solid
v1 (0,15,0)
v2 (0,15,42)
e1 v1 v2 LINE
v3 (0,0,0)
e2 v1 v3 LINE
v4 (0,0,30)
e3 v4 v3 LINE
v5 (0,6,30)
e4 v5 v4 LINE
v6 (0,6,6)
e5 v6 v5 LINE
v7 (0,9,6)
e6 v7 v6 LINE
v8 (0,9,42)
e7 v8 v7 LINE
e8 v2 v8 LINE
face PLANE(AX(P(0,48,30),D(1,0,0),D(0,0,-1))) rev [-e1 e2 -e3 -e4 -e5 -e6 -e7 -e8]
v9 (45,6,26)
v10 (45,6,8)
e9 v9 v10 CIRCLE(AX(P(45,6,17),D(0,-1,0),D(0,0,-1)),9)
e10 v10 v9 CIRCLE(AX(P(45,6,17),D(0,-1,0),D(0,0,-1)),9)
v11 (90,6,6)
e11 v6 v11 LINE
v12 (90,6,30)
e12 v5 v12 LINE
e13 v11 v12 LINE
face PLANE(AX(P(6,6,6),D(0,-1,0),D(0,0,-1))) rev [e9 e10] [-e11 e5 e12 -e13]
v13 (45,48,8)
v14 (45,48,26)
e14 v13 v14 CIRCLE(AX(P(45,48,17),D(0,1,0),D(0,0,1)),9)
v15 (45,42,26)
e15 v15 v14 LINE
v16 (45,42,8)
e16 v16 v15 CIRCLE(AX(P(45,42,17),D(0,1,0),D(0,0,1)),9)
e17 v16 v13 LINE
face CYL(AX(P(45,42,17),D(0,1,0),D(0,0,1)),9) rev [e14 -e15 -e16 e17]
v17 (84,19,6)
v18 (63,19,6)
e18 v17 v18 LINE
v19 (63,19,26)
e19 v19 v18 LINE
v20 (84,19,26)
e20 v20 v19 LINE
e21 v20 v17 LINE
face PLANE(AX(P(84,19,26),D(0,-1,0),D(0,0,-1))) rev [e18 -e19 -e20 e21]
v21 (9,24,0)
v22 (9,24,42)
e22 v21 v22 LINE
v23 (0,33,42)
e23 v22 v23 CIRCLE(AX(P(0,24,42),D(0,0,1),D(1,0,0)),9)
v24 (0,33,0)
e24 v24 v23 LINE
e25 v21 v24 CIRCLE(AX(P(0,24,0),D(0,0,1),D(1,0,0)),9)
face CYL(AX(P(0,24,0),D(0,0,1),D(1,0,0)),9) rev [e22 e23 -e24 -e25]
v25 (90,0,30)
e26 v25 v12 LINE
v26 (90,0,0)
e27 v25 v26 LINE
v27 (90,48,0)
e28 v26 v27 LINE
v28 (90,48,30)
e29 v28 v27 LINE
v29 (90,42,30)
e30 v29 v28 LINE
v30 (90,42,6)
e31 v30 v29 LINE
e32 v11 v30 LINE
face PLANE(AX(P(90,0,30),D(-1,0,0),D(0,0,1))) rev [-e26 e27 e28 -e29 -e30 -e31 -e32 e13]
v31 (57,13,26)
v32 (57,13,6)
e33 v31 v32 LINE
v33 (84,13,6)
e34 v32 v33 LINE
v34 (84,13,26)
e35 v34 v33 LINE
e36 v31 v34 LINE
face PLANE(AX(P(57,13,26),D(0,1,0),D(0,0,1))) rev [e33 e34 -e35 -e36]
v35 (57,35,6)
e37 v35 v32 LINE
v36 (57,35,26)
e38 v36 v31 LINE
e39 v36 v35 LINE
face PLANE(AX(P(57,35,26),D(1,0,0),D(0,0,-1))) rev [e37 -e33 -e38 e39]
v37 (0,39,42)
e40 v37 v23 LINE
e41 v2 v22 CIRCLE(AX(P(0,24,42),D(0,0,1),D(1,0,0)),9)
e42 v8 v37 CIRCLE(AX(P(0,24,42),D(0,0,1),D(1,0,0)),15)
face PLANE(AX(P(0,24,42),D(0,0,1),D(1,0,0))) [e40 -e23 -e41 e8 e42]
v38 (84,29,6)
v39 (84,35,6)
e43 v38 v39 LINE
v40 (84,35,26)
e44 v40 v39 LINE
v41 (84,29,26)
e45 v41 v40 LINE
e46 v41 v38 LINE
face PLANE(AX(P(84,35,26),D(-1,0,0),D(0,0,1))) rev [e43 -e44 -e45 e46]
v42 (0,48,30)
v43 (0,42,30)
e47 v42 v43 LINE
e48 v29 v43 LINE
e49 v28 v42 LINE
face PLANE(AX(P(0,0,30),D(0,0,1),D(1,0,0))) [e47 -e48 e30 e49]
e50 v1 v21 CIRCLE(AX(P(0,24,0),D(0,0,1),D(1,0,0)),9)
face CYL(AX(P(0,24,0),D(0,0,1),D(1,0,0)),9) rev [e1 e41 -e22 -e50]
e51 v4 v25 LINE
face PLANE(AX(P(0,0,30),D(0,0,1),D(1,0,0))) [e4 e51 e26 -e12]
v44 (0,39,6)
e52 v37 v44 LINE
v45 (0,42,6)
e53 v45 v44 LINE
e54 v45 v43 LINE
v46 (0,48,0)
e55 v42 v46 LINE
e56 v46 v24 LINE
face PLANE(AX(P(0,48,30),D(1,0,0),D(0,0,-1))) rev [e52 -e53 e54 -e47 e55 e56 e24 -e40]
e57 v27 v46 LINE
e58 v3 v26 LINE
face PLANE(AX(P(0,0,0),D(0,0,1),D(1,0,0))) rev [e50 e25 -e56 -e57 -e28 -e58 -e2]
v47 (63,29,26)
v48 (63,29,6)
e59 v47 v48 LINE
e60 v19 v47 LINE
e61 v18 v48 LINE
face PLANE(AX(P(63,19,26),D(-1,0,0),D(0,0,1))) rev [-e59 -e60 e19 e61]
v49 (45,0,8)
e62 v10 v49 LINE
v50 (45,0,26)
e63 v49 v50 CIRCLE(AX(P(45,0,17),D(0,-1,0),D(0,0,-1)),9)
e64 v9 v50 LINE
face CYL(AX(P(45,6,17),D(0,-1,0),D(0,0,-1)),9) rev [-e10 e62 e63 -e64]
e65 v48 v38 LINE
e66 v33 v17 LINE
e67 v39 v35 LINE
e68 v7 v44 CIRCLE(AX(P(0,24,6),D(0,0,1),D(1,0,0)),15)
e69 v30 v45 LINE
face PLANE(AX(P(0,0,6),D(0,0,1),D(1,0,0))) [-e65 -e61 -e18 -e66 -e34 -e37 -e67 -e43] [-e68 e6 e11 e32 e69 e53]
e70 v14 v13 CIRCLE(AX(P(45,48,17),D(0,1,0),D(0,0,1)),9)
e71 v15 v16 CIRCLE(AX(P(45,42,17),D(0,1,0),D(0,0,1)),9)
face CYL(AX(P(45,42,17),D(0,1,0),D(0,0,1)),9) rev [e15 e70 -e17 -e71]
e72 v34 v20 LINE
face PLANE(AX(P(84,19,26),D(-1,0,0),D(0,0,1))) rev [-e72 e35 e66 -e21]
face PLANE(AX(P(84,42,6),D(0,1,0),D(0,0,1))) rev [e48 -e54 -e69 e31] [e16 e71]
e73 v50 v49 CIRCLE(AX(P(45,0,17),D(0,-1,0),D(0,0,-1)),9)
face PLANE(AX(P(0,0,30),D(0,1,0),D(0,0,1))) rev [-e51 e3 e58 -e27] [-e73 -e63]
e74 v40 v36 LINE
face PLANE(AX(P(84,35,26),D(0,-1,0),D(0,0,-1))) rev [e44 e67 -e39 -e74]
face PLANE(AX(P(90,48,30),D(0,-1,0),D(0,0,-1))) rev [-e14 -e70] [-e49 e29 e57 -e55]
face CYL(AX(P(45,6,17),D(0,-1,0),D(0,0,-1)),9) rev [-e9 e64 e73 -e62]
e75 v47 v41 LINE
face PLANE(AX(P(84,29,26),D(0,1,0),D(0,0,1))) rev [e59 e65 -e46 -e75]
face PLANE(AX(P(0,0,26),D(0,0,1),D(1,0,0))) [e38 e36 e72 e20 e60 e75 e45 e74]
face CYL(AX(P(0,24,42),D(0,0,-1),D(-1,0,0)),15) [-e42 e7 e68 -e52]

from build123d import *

# Parameters (mm, degrees)
BASE_BLOCK_SKETCH_W           = 90
BASE_BLOCK_SKETCH_H           = 48
BASE_BLOCK_DEPTH              = 30
CHANNEL_SLOT_SKETCH_W         = 78
CHANNEL_SLOT_SKETCH_H         = 36
CHANNEL_SLOT_DEPTH            = 24
CHANNEL_RELIEF_CUT_1_SKETCH_W = 6
CHANNEL_RELIEF_CUT_1_SKETCH_H = 36
CHANNEL_RELIEF_CUT_1_DEPTH    = 24
CHANNEL_RELIEF_CUT_2_SKETCH_W = 6
CHANNEL_RELIEF_CUT_2_SKETCH_H = 36
CHANNEL_RELIEF_CUT_2_DEPTH    = 24
HALF_CYLINDER_BOSS_DEPTH      = 36
BOSS_BORE_18_DEPTH            = 42
UPPER_PLATE_HOLE_SKETCH_R     = 9
UPPER_PLATE_HOLE_18_DEPTH     = 6
LOWER_START                   = -6
LOWER_PLATE_HOLE_SKETCH_R     = 9
LOWER_PLATE_HOLE_18_DEPTH     = 6
C_CLIP_BOSS_DEPTH             = 20


with BuildPart() as part:
    # Base Block Sketch → Base Block (new body)
    with BuildSketch(Plane.XY):
        with Locations((45, 24)):
            Rectangle(BASE_BLOCK_SKETCH_W, BASE_BLOCK_SKETCH_H)
    extrude(amount=BASE_BLOCK_DEPTH)

    # Channel Slot Sketch → Channel Slot (cut)
    with BuildSketch(Plane.XY.offset(30)):
        with Locations((45, 24)):
            Rectangle(CHANNEL_SLOT_SKETCH_W, CHANNEL_SLOT_SKETCH_H)
    extrude(amount=-CHANNEL_SLOT_DEPTH, mode=Mode.SUBTRACT)

    # Channel Relief Cut 1 Sketch → Channel Relief Cut 1 (cut)
    with BuildSketch(Plane.XY.offset(30)):
        with Locations((3, 24)):
            Rectangle(CHANNEL_RELIEF_CUT_1_SKETCH_W, CHANNEL_RELIEF_CUT_1_SKETCH_H)
    extrude(amount=-CHANNEL_RELIEF_CUT_1_DEPTH, mode=Mode.SUBTRACT)

    # Channel Relief Cut 2 Sketch → Channel Relief Cut 2 (cut)
    with BuildSketch(Plane.XY.offset(30)):
        with Locations((87, 24)):
            Rectangle(CHANNEL_RELIEF_CUT_2_SKETCH_W, CHANNEL_RELIEF_CUT_2_SKETCH_H)
    extrude(amount=-CHANNEL_RELIEF_CUT_2_DEPTH, mode=Mode.SUBTRACT)

    # Half Cylinder Boss Sketch → Half Cylinder Boss (add)
    with BuildSketch(Plane.XY.offset(6)):
        with BuildLine():
            Line((0, 39), (0, 9))
            ThreePointArc((0, 9), (15, 24), (0, 39))
        make_face()
    extrude(amount=HALF_CYLINDER_BOSS_DEPTH)

    # Boss Bore Sketch → Boss Bore Ø18 (cut)
    with BuildSketch(Plane.XY.offset(42)):
        with BuildLine():
            Line((0, 33), (0, 15))
            ThreePointArc((0, 15), (9, 24), (0, 33))
        make_face()
    extrude(amount=-BOSS_BORE_18_DEPTH, mode=Mode.SUBTRACT)

    # Upper Plate Hole Sketch → Upper Plate Hole Ø18 (cut)
    with BuildSketch(Plane.XZ):
        with Locations(Location((45, 17, 0), (0, 0, 270))):
            Circle(UPPER_PLATE_HOLE_SKETCH_R)
    extrude(amount=-UPPER_PLATE_HOLE_18_DEPTH, mode=Mode.SUBTRACT)

    # Lower Plate Hole Sketch → Lower Plate Hole Ø18 (cut)
    with BuildSketch(Plane(origin=(0, 48, 0), x_dir=(1, 0, 0), z_dir=(0, 1, 0)).offset(LOWER_START)):
        with Locations(Location((45, -17, 0), (0, 0, 90))):
            Circle(LOWER_PLATE_HOLE_SKETCH_R)
    extrude(amount=LOWER_PLATE_HOLE_18_DEPTH, mode=Mode.SUBTRACT)

    # C Clip Boss Sketch → C Clip Boss (add)
    with BuildSketch(Plane.XY.offset(6)):
        Polygon((84, 35), (84, 29), (63, 29), (63, 19), (84, 19), (84, 13), (57, 13), (57, 35), align=None)
    extrude(amount=C_CLIP_BOSS_DEPTH)


solid = part.part
